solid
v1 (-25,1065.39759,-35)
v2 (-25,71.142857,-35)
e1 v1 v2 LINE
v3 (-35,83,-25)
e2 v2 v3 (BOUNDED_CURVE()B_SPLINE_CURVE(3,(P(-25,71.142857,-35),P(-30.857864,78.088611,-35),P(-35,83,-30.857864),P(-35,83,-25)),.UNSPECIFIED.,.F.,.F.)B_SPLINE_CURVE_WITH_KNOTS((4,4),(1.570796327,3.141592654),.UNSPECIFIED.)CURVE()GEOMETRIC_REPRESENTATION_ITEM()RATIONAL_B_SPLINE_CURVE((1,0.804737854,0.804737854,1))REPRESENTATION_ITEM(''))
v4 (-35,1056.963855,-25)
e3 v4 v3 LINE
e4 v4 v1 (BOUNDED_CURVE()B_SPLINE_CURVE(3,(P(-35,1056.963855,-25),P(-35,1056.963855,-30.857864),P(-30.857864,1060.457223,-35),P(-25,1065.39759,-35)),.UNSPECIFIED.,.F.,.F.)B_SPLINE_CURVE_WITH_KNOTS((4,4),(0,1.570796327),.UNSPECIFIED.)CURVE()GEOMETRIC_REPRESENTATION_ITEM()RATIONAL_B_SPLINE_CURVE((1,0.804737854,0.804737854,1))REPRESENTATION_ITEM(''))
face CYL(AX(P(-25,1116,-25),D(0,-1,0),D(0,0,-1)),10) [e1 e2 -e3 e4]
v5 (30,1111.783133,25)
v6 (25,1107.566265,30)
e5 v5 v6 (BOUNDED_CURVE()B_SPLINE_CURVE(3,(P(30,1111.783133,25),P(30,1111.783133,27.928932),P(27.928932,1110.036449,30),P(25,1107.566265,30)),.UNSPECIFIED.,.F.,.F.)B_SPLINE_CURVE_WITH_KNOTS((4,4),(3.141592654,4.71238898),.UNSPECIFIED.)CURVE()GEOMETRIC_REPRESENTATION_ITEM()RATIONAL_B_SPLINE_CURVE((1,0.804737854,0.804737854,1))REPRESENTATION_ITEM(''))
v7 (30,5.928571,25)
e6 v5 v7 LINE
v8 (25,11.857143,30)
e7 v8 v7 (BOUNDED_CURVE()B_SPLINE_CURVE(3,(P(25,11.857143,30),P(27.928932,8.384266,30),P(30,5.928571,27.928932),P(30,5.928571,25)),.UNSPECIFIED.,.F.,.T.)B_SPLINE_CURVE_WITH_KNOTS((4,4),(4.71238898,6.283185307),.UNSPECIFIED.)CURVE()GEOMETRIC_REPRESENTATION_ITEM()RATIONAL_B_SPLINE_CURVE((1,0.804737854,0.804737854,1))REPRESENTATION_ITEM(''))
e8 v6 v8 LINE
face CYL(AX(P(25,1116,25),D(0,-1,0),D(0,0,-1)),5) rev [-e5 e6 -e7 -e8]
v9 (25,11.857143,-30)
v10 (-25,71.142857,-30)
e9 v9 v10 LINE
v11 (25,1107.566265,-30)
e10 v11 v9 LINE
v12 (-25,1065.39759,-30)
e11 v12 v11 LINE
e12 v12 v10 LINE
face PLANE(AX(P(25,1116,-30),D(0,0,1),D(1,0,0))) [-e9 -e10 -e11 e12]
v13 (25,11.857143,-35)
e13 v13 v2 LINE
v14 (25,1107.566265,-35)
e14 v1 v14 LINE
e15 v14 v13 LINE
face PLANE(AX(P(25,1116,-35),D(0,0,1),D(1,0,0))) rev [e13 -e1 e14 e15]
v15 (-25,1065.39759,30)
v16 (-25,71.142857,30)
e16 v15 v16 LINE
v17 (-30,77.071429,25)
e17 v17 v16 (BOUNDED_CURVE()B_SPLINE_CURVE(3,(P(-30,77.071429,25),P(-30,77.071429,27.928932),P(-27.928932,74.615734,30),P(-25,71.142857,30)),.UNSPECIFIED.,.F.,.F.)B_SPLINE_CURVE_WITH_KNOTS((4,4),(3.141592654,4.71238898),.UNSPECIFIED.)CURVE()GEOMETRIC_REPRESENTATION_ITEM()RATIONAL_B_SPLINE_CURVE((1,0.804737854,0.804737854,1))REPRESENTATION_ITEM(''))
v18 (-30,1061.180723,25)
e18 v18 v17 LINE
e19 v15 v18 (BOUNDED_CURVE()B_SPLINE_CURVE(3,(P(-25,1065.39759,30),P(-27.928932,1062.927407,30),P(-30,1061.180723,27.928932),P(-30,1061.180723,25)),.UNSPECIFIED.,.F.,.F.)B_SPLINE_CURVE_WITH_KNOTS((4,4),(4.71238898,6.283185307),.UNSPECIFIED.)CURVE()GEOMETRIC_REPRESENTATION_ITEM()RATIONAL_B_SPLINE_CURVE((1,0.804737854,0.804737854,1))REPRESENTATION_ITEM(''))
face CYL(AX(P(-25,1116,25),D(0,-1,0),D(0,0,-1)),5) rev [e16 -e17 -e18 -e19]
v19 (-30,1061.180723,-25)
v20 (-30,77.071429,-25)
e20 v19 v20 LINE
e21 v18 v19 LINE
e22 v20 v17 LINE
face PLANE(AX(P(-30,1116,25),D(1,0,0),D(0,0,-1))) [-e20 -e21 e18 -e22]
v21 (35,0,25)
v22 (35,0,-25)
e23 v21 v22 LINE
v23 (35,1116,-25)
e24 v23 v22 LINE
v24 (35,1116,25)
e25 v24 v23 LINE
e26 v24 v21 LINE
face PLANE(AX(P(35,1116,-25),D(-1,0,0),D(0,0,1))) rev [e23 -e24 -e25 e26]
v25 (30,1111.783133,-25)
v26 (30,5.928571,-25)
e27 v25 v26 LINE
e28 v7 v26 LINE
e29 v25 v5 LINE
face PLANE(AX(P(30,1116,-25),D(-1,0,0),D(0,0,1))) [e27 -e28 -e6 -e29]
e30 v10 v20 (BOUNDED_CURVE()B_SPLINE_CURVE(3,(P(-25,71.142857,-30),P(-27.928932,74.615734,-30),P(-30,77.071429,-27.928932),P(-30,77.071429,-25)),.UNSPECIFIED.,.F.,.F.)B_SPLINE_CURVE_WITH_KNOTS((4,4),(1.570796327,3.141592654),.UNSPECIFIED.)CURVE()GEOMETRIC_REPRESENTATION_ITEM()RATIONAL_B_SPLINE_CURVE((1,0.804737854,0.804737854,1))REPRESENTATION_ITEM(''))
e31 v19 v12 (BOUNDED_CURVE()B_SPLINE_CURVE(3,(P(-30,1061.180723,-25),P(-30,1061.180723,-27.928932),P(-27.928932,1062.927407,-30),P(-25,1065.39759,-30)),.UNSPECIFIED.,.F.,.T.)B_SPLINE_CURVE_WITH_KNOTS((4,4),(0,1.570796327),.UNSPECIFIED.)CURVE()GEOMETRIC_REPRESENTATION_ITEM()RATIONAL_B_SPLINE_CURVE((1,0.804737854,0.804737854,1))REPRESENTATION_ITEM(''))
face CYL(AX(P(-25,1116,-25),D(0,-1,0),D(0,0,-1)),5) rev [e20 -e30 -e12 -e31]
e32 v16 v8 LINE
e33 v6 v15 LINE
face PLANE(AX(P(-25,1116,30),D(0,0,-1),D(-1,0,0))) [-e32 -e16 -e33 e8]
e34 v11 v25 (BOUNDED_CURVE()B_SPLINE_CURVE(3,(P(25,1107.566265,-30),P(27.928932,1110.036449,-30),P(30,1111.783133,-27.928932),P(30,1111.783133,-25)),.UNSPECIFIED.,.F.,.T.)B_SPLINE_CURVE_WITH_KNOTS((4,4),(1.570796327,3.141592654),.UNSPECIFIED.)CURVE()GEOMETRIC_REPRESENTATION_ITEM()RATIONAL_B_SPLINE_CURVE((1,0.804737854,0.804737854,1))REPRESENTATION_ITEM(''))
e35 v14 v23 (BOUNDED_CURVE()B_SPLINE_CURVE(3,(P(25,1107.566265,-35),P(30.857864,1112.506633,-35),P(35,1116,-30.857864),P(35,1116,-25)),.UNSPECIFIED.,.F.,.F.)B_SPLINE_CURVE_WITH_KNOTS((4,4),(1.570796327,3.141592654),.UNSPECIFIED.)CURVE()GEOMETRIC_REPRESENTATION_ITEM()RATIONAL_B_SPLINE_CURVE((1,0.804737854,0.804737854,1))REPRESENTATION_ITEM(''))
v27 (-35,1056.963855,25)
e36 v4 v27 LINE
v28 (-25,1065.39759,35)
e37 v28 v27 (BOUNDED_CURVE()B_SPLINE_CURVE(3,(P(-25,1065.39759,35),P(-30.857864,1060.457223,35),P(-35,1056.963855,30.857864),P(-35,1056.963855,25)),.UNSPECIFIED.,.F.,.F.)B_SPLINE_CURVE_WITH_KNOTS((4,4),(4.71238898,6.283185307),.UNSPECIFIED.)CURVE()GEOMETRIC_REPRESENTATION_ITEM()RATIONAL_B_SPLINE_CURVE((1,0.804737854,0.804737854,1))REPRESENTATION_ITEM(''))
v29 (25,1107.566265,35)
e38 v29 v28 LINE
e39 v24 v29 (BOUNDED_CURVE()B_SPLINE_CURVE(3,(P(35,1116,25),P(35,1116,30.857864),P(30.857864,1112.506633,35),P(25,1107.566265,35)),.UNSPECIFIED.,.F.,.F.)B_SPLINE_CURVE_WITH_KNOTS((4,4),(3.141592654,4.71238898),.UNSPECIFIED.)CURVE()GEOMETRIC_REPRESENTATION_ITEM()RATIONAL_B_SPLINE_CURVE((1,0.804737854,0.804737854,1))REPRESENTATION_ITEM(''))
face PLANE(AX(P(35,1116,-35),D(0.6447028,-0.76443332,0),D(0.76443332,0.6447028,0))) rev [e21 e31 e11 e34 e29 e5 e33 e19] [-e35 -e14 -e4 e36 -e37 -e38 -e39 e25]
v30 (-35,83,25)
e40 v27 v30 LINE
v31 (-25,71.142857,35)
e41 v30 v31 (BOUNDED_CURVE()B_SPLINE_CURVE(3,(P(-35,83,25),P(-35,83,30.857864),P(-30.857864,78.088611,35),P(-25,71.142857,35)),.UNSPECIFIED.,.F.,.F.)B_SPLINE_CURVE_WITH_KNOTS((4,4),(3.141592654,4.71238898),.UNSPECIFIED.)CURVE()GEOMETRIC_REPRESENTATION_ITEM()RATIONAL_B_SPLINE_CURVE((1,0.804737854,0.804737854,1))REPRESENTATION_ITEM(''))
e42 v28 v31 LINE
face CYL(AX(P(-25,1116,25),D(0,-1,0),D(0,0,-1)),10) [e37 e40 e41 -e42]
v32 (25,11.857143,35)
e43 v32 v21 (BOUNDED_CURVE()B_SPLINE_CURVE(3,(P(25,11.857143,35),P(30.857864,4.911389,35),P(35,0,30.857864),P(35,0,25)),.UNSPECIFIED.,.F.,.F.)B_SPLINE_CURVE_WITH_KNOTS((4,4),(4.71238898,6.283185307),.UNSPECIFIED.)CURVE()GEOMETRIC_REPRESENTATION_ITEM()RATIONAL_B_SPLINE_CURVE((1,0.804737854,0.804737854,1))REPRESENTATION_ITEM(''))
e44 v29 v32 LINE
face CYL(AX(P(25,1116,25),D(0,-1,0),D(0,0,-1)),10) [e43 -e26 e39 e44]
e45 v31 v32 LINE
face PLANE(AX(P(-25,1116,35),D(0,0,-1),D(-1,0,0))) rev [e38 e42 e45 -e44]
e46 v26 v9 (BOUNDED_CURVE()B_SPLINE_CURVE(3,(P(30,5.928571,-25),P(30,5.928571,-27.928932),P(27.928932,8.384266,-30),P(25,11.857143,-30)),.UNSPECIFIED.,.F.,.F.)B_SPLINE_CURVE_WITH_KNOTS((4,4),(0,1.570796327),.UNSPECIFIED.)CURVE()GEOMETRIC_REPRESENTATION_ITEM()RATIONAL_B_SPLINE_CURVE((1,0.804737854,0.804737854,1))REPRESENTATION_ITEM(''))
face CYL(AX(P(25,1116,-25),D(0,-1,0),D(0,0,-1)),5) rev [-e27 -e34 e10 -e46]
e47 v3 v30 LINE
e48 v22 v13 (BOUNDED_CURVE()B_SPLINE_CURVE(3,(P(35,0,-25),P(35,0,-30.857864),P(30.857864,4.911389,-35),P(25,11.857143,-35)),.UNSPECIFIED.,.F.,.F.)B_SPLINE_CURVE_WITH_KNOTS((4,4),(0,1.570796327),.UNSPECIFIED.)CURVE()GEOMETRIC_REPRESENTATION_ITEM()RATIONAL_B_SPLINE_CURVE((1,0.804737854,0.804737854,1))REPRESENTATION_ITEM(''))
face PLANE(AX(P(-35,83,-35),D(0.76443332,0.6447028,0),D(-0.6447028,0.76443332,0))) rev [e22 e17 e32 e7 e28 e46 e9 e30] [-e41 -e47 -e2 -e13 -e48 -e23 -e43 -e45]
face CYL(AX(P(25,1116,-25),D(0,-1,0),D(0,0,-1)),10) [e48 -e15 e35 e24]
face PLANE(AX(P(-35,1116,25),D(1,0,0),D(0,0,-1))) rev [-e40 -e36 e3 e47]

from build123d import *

# Parameters (mm, degrees)
GB_T6728_2002_70_70_5_1_DEPTH = 1116
CUT_EXTRUDE_1_DEPTH           = 1119.740810018
CUT_EXTRUDE_1_DEPTH_BACK      = 1119.740810018


with BuildPart() as part:
    # Sketch1 → 结构用冷弯空心方钢(gb t6728-2002) 70×70×5(1) (new body)
    with BuildSketch(Plane(origin=(0, 0, 0), x_dir=(-1, 0, 0), z_dir=(0, 1, 0))):
        with BuildLine():
            Line((-25, -35), (25, -35))
            ThreePointArc((25, -35), (32.071067812, -32.071067812), (35, -25))
            Line((35, -25), (35, 25))
            ThreePointArc((35, 25), (32.071067812, 32.071067812), (25, 35))
            Line((25, 35), (-25, 35))
            ThreePointArc((-25, 35), (-32.071067812, 32.071067812), (-35, 25))
            Line((-35, 25), (-35, -25))
            ThreePointArc((-35, -25), (-32.071067812, -32.071067812), (-25, -35))
        make_face()
        with BuildLine():
            Line((-25, -30), (25, -30))
            ThreePointArc((25, -30), (28.535533906, -28.535533906), (30, -25))
            Line((30, -25), (30, 25))
            ThreePointArc((30, 25), (28.535533906, 28.535533906), (25, 30))
            Line((25, 30), (-25, 30))
            ThreePointArc((-25, 30), (-28.535533906, 28.535533906), (-30, 25))
            Line((-30, 25), (-30, -25))
            ThreePointArc((-30, -25), (-28.535533906, -28.535533906), (-25, -30))
        make_face(mode=Mode.SUBTRACT)
    extrude(amount=GB_T6728_2002_70_70_5_1_DEPTH)

    # 草图2 → 切除-拉伸1 (cut, two sides: drawn at the far end of the back side and taken through both)
    with BuildSketch(Plane.XY.offset(35).offset(-CUT_EXTRUDE_1_DEPTH_BACK)):
        Polygon((35, 1116), (-35, 1056.963855422), (-35, 1116), align=None)
        Polygon((-35, 83), (35, 0), (-35, 0), align=None)
    extrude(amount=CUT_EXTRUDE_1_DEPTH + CUT_EXTRUDE_1_DEPTH_BACK, mode=Mode.SUBTRACT)


solid = part.part
